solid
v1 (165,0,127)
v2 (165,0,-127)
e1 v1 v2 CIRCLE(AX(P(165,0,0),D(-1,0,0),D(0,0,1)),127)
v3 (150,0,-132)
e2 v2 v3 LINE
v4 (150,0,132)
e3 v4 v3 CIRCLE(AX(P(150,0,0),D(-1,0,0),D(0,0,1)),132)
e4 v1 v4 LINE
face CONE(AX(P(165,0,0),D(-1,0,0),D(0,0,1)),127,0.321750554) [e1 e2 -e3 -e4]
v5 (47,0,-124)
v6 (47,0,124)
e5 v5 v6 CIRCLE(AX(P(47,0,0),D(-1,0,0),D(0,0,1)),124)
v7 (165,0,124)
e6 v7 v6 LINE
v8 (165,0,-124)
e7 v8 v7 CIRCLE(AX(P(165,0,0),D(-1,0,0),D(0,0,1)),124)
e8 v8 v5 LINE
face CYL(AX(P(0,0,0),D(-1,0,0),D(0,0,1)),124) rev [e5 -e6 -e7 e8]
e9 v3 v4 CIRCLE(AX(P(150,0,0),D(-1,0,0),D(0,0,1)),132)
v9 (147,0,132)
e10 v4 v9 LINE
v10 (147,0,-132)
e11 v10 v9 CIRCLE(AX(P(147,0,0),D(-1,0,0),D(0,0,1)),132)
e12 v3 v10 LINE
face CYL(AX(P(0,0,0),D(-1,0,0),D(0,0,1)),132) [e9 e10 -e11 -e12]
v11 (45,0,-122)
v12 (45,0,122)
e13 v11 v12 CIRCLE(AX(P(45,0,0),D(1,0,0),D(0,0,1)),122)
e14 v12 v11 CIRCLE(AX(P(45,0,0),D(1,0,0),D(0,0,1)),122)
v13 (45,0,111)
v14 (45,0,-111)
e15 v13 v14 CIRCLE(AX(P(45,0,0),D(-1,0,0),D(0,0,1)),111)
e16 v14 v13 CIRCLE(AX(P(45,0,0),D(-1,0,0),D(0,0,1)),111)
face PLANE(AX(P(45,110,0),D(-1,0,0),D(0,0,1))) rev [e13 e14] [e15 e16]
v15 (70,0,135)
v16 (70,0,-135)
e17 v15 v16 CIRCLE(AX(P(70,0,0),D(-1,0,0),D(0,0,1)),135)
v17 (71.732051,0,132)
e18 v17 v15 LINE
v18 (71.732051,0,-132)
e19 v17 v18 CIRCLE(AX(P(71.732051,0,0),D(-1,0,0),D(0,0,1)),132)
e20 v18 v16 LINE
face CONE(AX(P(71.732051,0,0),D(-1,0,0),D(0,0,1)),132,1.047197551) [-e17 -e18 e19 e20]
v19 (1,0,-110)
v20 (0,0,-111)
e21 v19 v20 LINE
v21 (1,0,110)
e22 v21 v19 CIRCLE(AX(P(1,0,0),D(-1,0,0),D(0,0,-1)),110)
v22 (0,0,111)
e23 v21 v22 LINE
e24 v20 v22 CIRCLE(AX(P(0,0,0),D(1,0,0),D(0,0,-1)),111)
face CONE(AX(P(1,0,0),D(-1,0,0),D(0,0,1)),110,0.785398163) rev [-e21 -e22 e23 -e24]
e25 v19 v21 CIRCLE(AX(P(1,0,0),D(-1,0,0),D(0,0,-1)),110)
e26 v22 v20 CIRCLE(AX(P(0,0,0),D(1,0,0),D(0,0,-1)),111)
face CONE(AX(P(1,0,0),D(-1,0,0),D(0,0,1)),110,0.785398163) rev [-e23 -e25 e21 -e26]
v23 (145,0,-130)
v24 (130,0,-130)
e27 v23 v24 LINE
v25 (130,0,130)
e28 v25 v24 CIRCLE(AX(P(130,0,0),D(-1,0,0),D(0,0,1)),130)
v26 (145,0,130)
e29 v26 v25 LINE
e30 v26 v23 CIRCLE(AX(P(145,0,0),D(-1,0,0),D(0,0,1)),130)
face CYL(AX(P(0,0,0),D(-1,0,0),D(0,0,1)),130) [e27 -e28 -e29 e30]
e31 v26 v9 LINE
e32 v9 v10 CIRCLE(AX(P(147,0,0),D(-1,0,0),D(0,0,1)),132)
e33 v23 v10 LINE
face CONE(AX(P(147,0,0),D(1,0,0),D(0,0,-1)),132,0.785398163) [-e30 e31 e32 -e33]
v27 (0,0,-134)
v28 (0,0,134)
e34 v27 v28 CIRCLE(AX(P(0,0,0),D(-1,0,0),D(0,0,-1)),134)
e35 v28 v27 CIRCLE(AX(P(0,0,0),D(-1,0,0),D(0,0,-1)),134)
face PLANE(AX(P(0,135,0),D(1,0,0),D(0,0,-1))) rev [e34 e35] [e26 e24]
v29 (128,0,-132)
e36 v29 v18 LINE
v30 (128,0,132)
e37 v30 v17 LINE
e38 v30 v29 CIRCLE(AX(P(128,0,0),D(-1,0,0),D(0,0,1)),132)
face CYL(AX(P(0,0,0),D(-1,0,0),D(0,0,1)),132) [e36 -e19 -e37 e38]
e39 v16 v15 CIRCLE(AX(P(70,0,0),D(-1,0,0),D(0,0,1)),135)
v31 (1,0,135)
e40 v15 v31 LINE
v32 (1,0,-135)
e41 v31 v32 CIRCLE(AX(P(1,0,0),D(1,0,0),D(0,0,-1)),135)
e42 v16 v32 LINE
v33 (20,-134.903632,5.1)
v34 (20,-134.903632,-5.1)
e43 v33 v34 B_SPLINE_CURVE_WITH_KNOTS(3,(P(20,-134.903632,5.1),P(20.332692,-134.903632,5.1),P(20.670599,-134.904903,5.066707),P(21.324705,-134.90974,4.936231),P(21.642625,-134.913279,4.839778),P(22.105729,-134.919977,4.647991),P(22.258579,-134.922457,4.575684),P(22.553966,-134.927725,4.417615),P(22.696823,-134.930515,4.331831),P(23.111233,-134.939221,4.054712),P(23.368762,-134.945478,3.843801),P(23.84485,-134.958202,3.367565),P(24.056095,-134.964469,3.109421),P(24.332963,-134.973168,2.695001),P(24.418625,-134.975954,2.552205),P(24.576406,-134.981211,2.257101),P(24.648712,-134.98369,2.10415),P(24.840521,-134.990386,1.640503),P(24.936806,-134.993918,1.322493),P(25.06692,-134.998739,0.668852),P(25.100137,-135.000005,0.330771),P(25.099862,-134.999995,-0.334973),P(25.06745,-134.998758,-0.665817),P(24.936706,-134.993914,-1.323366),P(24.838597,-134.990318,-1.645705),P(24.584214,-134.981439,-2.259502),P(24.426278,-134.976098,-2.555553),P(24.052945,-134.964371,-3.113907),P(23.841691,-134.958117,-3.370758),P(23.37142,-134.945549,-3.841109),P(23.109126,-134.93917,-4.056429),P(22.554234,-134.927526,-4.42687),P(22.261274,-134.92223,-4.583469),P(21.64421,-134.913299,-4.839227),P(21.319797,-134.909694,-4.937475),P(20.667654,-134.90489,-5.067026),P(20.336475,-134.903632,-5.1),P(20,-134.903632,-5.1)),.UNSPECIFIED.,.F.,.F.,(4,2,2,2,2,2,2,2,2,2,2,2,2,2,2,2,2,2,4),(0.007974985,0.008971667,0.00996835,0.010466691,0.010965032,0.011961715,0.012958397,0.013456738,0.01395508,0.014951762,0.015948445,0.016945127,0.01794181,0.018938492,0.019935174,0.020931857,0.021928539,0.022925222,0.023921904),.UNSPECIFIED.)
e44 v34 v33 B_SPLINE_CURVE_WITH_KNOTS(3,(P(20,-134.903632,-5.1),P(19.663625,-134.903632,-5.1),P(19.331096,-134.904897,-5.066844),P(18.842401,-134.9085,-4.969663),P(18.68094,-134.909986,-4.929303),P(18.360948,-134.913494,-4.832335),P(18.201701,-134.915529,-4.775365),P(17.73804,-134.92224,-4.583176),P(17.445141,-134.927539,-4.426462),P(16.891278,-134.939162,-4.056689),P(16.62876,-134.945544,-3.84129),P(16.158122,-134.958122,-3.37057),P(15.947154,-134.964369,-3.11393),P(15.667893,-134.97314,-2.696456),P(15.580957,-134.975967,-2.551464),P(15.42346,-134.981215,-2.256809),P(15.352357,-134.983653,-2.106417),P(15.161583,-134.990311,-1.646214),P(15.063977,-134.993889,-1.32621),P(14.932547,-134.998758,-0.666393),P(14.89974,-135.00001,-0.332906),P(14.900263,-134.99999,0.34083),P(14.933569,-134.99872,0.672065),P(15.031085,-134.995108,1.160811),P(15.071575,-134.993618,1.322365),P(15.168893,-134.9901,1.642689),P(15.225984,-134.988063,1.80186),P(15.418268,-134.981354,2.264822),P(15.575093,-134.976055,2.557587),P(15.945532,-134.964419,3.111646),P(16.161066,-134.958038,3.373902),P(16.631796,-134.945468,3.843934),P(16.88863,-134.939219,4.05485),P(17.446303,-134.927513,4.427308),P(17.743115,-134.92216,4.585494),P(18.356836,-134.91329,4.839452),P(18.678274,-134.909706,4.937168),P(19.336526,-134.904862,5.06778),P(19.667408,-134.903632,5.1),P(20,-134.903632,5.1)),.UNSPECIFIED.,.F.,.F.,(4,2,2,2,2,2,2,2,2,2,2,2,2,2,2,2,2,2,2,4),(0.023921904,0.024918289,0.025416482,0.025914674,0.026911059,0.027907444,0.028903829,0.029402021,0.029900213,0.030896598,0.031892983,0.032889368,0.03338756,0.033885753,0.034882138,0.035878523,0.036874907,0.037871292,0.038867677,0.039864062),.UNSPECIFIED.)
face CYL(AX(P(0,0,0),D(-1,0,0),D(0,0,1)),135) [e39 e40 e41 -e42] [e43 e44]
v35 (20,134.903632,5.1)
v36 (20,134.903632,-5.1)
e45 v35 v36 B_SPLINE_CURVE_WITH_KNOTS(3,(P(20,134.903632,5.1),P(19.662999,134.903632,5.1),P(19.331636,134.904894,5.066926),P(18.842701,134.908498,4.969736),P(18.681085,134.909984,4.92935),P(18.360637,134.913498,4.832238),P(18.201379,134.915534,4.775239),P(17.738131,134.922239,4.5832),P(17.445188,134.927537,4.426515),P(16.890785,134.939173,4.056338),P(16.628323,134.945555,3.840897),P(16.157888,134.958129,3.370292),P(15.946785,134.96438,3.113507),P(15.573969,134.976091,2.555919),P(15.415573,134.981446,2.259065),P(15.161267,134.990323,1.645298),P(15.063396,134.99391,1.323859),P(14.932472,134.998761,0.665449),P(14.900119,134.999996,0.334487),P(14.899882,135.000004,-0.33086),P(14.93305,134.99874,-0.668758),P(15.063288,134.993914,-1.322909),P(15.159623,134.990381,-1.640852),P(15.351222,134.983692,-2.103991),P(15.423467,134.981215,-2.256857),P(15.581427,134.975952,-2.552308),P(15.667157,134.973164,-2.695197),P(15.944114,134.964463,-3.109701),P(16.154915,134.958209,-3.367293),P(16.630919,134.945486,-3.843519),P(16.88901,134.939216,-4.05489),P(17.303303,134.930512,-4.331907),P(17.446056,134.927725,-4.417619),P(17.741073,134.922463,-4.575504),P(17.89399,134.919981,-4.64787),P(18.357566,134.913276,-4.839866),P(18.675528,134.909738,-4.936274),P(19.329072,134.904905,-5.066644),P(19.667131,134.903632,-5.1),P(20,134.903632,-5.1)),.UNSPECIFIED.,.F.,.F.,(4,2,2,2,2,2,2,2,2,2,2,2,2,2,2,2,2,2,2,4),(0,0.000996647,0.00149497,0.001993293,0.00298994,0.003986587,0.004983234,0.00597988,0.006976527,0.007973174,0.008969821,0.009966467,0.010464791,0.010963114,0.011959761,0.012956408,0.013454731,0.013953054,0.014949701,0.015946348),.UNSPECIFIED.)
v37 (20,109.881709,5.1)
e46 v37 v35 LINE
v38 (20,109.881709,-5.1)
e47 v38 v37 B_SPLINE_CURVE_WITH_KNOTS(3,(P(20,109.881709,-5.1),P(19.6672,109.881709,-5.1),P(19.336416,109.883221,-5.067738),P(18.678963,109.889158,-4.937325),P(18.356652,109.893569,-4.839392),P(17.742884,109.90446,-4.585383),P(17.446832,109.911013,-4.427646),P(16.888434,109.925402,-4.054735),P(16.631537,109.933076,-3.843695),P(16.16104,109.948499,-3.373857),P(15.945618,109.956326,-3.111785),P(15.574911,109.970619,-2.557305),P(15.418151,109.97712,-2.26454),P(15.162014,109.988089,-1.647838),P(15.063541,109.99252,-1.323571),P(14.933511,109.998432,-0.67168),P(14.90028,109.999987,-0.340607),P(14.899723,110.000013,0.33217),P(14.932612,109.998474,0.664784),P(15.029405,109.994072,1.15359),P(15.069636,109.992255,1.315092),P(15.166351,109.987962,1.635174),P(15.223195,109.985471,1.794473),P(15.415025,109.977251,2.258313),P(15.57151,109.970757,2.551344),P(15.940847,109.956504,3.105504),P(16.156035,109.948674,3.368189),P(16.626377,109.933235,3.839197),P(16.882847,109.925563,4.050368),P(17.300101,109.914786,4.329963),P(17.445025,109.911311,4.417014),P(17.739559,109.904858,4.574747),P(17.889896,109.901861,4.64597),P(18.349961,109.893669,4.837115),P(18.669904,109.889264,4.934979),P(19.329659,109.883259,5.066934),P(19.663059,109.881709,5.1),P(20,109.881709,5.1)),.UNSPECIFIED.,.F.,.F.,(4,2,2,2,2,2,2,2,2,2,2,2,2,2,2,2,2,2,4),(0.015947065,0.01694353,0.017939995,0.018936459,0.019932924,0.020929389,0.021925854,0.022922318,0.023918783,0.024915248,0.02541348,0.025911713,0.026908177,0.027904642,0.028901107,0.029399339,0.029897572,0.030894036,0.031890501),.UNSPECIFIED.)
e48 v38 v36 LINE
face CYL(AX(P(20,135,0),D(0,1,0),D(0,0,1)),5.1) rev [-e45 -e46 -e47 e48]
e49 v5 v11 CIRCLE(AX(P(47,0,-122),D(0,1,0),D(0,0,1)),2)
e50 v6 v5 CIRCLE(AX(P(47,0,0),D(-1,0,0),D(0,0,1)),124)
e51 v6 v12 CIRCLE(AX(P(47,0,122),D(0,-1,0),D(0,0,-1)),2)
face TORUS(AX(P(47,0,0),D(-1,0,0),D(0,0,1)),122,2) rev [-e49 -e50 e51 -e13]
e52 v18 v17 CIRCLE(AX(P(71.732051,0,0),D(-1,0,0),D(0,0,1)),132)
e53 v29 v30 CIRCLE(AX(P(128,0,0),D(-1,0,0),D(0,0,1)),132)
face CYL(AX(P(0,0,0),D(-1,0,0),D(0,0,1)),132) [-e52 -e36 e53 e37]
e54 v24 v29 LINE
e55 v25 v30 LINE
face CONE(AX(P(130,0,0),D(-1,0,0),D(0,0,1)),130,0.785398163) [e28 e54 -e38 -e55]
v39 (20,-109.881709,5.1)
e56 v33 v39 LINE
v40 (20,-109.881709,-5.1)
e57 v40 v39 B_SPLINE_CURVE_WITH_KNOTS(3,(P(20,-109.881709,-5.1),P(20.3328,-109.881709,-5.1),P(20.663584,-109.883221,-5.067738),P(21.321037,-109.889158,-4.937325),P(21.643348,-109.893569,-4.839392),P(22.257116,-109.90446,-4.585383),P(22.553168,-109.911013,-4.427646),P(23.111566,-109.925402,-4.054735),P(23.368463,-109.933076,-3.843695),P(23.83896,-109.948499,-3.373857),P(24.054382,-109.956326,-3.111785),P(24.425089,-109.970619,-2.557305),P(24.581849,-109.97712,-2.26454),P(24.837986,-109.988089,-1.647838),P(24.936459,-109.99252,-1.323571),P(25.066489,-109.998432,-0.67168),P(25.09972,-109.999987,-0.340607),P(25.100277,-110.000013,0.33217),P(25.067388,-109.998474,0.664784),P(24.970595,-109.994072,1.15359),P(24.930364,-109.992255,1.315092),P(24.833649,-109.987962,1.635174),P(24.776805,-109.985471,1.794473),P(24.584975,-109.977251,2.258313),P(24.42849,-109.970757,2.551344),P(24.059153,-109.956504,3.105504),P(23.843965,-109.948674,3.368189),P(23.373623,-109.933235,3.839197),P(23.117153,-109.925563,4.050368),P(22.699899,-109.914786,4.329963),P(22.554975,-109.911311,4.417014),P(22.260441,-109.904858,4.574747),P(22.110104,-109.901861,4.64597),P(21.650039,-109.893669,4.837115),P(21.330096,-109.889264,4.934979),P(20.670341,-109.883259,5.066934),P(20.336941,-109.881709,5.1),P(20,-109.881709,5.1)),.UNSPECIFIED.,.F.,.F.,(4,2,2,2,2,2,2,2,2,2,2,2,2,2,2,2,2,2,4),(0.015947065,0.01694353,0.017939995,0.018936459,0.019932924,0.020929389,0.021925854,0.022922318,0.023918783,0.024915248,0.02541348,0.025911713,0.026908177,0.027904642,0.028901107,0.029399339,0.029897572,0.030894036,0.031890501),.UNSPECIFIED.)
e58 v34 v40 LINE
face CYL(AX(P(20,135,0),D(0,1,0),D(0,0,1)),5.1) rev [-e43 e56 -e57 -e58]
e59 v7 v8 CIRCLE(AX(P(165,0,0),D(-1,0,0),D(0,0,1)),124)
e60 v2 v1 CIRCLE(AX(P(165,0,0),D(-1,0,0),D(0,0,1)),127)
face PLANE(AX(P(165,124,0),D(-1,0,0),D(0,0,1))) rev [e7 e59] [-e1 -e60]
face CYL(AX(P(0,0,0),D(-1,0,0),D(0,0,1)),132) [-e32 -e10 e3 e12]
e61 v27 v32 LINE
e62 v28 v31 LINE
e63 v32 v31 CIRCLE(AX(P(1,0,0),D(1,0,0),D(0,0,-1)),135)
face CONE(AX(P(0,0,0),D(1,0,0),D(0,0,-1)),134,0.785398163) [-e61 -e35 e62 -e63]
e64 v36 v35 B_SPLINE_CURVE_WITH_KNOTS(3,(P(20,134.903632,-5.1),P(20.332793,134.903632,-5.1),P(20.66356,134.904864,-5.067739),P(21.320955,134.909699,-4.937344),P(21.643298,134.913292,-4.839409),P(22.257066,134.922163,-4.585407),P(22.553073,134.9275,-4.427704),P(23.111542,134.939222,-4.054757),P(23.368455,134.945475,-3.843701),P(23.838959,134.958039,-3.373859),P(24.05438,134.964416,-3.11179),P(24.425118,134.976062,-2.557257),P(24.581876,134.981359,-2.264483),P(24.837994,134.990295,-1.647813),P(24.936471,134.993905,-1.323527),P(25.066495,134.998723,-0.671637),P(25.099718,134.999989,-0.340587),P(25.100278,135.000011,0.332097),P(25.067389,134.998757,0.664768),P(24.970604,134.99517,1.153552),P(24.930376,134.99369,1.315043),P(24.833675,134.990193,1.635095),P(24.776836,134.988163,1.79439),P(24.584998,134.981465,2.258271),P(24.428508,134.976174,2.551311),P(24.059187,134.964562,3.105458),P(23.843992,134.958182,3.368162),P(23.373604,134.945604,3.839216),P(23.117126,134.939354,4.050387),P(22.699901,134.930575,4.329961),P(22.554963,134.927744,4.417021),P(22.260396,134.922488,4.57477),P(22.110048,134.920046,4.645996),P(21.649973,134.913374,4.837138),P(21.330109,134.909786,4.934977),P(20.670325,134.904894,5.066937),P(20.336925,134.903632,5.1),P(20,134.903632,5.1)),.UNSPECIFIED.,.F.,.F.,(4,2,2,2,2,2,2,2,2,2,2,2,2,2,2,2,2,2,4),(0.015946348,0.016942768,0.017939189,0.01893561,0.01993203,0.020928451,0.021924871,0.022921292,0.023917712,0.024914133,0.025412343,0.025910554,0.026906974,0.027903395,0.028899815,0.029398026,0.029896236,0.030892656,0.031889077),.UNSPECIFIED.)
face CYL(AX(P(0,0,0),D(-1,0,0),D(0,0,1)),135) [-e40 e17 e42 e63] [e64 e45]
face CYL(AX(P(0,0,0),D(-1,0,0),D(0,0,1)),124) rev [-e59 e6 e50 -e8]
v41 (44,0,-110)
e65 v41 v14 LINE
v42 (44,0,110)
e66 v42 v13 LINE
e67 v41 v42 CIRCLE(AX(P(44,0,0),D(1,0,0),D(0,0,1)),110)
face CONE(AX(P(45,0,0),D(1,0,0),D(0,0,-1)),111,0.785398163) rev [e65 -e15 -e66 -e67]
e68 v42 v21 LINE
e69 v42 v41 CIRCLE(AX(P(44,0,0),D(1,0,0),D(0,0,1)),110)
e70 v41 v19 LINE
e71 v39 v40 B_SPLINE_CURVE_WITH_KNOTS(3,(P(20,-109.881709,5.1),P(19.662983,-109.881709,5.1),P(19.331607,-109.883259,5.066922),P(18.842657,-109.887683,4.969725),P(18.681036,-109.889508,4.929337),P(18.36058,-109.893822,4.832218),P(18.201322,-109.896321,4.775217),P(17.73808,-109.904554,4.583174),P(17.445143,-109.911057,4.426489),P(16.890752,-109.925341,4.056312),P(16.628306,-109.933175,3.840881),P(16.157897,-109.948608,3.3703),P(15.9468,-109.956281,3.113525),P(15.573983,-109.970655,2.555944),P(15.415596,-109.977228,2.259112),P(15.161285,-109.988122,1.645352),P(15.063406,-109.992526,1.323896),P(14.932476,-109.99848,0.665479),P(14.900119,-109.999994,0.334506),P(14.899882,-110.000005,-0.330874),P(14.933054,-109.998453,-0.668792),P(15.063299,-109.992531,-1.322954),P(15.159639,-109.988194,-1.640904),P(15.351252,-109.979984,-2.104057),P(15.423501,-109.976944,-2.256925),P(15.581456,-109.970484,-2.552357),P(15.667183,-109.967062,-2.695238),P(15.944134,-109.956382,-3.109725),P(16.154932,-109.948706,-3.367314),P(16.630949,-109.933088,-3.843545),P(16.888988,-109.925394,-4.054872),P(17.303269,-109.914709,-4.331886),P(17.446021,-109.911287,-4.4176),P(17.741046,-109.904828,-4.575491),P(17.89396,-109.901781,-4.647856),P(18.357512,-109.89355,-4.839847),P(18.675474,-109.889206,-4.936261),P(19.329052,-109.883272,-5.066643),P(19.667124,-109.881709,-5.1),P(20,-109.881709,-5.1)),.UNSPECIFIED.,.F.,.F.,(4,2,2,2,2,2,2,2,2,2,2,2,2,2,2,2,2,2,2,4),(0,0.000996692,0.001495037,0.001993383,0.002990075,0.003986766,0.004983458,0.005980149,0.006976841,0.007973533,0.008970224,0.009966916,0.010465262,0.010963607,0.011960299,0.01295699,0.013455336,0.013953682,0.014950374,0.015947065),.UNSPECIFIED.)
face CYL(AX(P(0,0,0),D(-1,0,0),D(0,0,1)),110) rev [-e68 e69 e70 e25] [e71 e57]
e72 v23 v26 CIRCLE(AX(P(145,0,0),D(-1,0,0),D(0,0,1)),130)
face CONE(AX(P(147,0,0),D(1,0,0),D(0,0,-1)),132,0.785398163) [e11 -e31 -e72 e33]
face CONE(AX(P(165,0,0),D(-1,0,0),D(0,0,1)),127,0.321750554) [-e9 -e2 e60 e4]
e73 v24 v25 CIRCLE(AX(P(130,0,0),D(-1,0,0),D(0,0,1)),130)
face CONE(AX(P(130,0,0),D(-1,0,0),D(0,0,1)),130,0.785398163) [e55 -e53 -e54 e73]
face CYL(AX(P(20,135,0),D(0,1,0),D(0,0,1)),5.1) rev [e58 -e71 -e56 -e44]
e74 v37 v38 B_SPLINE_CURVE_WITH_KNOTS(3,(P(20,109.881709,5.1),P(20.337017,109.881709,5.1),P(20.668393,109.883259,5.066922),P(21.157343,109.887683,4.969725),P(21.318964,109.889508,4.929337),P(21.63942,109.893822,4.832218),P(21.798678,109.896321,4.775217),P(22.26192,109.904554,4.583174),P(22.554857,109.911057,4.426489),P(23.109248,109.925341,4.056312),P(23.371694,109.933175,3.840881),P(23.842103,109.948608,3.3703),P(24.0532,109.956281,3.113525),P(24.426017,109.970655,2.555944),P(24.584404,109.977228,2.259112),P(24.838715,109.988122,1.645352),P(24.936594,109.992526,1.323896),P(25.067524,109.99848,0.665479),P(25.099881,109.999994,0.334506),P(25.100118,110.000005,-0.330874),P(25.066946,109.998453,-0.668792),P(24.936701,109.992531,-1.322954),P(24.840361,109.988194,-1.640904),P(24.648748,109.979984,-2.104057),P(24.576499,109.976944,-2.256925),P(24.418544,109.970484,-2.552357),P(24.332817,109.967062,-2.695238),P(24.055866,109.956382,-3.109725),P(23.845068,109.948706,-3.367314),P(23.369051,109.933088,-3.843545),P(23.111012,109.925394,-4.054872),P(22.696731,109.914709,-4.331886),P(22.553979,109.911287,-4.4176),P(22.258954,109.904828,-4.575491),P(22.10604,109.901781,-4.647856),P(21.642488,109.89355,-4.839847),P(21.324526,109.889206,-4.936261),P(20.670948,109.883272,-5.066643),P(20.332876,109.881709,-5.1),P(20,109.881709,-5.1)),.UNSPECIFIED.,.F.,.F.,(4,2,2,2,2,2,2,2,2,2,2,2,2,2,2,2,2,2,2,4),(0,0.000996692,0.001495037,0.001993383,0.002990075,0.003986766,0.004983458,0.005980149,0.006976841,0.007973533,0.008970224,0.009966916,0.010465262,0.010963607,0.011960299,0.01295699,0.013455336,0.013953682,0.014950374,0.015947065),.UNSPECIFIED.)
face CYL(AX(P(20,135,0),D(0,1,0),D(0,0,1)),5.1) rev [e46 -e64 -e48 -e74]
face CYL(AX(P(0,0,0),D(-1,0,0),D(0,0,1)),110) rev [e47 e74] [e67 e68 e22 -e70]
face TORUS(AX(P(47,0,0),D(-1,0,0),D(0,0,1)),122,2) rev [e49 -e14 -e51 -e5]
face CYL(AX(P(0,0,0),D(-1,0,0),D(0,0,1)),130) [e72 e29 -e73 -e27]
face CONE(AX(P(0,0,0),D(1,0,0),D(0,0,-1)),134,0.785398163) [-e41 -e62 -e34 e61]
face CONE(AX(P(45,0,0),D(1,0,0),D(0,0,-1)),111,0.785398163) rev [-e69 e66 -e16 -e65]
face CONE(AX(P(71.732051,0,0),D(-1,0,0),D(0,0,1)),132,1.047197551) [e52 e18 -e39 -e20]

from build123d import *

# Parameters (mm, degrees)
FILLET1_R          = 2
CHAMFER1_SIZE      = 1
M12_TAPPED_HOLE1_D = 10.2


with BuildPart() as part:
    # Sketch1 → Revolve1 (revolve)
    with BuildSketch(Plane.XY, mode=Mode.PRIVATE) as revolve1_sk:
        Polygon((0, 110), (45, 110), (45, 124), (165, 124), (165, 127), (150, 132), (147, 132), (145, 130), (130, 130), (128, 132), (71.732050808, 132), (70, 135), (0, 135), align=None)
    revolve(revolve1_sk.sketch.rotate(Axis((0, 0, 0), (1, 0, 0)), 90), axis=Axis((0, 0, 0), (1, 0, 0)))

    # Fillet1
    fillet1_edges = [part.edges().sort_by_distance(p)[0] for p in [
        (45, 0, -124),
    ]]
    fillet(fillet1_edges, radius=FILLET1_R)

    # Chamfer1
    chamfer1_edges = [part.edges().sort_by_distance(p)[0] for p in [
        (45, 0, -110),
        (0, 0, -110),
        (0, 0, -135),
    ]]
    chamfer(chamfer1_edges, length=CHAMFER1_SIZE)

    # M12 Tapped Hole1 (through all)
    with Locations(Plane(origin=(20, 135, 0), x_dir=(0, 0, 1), z_dir=(0, 1, 0))):
        with Locations((0, 0)):
            Hole(M12_TAPPED_HOLE1_D / 2)


solid = part.part
